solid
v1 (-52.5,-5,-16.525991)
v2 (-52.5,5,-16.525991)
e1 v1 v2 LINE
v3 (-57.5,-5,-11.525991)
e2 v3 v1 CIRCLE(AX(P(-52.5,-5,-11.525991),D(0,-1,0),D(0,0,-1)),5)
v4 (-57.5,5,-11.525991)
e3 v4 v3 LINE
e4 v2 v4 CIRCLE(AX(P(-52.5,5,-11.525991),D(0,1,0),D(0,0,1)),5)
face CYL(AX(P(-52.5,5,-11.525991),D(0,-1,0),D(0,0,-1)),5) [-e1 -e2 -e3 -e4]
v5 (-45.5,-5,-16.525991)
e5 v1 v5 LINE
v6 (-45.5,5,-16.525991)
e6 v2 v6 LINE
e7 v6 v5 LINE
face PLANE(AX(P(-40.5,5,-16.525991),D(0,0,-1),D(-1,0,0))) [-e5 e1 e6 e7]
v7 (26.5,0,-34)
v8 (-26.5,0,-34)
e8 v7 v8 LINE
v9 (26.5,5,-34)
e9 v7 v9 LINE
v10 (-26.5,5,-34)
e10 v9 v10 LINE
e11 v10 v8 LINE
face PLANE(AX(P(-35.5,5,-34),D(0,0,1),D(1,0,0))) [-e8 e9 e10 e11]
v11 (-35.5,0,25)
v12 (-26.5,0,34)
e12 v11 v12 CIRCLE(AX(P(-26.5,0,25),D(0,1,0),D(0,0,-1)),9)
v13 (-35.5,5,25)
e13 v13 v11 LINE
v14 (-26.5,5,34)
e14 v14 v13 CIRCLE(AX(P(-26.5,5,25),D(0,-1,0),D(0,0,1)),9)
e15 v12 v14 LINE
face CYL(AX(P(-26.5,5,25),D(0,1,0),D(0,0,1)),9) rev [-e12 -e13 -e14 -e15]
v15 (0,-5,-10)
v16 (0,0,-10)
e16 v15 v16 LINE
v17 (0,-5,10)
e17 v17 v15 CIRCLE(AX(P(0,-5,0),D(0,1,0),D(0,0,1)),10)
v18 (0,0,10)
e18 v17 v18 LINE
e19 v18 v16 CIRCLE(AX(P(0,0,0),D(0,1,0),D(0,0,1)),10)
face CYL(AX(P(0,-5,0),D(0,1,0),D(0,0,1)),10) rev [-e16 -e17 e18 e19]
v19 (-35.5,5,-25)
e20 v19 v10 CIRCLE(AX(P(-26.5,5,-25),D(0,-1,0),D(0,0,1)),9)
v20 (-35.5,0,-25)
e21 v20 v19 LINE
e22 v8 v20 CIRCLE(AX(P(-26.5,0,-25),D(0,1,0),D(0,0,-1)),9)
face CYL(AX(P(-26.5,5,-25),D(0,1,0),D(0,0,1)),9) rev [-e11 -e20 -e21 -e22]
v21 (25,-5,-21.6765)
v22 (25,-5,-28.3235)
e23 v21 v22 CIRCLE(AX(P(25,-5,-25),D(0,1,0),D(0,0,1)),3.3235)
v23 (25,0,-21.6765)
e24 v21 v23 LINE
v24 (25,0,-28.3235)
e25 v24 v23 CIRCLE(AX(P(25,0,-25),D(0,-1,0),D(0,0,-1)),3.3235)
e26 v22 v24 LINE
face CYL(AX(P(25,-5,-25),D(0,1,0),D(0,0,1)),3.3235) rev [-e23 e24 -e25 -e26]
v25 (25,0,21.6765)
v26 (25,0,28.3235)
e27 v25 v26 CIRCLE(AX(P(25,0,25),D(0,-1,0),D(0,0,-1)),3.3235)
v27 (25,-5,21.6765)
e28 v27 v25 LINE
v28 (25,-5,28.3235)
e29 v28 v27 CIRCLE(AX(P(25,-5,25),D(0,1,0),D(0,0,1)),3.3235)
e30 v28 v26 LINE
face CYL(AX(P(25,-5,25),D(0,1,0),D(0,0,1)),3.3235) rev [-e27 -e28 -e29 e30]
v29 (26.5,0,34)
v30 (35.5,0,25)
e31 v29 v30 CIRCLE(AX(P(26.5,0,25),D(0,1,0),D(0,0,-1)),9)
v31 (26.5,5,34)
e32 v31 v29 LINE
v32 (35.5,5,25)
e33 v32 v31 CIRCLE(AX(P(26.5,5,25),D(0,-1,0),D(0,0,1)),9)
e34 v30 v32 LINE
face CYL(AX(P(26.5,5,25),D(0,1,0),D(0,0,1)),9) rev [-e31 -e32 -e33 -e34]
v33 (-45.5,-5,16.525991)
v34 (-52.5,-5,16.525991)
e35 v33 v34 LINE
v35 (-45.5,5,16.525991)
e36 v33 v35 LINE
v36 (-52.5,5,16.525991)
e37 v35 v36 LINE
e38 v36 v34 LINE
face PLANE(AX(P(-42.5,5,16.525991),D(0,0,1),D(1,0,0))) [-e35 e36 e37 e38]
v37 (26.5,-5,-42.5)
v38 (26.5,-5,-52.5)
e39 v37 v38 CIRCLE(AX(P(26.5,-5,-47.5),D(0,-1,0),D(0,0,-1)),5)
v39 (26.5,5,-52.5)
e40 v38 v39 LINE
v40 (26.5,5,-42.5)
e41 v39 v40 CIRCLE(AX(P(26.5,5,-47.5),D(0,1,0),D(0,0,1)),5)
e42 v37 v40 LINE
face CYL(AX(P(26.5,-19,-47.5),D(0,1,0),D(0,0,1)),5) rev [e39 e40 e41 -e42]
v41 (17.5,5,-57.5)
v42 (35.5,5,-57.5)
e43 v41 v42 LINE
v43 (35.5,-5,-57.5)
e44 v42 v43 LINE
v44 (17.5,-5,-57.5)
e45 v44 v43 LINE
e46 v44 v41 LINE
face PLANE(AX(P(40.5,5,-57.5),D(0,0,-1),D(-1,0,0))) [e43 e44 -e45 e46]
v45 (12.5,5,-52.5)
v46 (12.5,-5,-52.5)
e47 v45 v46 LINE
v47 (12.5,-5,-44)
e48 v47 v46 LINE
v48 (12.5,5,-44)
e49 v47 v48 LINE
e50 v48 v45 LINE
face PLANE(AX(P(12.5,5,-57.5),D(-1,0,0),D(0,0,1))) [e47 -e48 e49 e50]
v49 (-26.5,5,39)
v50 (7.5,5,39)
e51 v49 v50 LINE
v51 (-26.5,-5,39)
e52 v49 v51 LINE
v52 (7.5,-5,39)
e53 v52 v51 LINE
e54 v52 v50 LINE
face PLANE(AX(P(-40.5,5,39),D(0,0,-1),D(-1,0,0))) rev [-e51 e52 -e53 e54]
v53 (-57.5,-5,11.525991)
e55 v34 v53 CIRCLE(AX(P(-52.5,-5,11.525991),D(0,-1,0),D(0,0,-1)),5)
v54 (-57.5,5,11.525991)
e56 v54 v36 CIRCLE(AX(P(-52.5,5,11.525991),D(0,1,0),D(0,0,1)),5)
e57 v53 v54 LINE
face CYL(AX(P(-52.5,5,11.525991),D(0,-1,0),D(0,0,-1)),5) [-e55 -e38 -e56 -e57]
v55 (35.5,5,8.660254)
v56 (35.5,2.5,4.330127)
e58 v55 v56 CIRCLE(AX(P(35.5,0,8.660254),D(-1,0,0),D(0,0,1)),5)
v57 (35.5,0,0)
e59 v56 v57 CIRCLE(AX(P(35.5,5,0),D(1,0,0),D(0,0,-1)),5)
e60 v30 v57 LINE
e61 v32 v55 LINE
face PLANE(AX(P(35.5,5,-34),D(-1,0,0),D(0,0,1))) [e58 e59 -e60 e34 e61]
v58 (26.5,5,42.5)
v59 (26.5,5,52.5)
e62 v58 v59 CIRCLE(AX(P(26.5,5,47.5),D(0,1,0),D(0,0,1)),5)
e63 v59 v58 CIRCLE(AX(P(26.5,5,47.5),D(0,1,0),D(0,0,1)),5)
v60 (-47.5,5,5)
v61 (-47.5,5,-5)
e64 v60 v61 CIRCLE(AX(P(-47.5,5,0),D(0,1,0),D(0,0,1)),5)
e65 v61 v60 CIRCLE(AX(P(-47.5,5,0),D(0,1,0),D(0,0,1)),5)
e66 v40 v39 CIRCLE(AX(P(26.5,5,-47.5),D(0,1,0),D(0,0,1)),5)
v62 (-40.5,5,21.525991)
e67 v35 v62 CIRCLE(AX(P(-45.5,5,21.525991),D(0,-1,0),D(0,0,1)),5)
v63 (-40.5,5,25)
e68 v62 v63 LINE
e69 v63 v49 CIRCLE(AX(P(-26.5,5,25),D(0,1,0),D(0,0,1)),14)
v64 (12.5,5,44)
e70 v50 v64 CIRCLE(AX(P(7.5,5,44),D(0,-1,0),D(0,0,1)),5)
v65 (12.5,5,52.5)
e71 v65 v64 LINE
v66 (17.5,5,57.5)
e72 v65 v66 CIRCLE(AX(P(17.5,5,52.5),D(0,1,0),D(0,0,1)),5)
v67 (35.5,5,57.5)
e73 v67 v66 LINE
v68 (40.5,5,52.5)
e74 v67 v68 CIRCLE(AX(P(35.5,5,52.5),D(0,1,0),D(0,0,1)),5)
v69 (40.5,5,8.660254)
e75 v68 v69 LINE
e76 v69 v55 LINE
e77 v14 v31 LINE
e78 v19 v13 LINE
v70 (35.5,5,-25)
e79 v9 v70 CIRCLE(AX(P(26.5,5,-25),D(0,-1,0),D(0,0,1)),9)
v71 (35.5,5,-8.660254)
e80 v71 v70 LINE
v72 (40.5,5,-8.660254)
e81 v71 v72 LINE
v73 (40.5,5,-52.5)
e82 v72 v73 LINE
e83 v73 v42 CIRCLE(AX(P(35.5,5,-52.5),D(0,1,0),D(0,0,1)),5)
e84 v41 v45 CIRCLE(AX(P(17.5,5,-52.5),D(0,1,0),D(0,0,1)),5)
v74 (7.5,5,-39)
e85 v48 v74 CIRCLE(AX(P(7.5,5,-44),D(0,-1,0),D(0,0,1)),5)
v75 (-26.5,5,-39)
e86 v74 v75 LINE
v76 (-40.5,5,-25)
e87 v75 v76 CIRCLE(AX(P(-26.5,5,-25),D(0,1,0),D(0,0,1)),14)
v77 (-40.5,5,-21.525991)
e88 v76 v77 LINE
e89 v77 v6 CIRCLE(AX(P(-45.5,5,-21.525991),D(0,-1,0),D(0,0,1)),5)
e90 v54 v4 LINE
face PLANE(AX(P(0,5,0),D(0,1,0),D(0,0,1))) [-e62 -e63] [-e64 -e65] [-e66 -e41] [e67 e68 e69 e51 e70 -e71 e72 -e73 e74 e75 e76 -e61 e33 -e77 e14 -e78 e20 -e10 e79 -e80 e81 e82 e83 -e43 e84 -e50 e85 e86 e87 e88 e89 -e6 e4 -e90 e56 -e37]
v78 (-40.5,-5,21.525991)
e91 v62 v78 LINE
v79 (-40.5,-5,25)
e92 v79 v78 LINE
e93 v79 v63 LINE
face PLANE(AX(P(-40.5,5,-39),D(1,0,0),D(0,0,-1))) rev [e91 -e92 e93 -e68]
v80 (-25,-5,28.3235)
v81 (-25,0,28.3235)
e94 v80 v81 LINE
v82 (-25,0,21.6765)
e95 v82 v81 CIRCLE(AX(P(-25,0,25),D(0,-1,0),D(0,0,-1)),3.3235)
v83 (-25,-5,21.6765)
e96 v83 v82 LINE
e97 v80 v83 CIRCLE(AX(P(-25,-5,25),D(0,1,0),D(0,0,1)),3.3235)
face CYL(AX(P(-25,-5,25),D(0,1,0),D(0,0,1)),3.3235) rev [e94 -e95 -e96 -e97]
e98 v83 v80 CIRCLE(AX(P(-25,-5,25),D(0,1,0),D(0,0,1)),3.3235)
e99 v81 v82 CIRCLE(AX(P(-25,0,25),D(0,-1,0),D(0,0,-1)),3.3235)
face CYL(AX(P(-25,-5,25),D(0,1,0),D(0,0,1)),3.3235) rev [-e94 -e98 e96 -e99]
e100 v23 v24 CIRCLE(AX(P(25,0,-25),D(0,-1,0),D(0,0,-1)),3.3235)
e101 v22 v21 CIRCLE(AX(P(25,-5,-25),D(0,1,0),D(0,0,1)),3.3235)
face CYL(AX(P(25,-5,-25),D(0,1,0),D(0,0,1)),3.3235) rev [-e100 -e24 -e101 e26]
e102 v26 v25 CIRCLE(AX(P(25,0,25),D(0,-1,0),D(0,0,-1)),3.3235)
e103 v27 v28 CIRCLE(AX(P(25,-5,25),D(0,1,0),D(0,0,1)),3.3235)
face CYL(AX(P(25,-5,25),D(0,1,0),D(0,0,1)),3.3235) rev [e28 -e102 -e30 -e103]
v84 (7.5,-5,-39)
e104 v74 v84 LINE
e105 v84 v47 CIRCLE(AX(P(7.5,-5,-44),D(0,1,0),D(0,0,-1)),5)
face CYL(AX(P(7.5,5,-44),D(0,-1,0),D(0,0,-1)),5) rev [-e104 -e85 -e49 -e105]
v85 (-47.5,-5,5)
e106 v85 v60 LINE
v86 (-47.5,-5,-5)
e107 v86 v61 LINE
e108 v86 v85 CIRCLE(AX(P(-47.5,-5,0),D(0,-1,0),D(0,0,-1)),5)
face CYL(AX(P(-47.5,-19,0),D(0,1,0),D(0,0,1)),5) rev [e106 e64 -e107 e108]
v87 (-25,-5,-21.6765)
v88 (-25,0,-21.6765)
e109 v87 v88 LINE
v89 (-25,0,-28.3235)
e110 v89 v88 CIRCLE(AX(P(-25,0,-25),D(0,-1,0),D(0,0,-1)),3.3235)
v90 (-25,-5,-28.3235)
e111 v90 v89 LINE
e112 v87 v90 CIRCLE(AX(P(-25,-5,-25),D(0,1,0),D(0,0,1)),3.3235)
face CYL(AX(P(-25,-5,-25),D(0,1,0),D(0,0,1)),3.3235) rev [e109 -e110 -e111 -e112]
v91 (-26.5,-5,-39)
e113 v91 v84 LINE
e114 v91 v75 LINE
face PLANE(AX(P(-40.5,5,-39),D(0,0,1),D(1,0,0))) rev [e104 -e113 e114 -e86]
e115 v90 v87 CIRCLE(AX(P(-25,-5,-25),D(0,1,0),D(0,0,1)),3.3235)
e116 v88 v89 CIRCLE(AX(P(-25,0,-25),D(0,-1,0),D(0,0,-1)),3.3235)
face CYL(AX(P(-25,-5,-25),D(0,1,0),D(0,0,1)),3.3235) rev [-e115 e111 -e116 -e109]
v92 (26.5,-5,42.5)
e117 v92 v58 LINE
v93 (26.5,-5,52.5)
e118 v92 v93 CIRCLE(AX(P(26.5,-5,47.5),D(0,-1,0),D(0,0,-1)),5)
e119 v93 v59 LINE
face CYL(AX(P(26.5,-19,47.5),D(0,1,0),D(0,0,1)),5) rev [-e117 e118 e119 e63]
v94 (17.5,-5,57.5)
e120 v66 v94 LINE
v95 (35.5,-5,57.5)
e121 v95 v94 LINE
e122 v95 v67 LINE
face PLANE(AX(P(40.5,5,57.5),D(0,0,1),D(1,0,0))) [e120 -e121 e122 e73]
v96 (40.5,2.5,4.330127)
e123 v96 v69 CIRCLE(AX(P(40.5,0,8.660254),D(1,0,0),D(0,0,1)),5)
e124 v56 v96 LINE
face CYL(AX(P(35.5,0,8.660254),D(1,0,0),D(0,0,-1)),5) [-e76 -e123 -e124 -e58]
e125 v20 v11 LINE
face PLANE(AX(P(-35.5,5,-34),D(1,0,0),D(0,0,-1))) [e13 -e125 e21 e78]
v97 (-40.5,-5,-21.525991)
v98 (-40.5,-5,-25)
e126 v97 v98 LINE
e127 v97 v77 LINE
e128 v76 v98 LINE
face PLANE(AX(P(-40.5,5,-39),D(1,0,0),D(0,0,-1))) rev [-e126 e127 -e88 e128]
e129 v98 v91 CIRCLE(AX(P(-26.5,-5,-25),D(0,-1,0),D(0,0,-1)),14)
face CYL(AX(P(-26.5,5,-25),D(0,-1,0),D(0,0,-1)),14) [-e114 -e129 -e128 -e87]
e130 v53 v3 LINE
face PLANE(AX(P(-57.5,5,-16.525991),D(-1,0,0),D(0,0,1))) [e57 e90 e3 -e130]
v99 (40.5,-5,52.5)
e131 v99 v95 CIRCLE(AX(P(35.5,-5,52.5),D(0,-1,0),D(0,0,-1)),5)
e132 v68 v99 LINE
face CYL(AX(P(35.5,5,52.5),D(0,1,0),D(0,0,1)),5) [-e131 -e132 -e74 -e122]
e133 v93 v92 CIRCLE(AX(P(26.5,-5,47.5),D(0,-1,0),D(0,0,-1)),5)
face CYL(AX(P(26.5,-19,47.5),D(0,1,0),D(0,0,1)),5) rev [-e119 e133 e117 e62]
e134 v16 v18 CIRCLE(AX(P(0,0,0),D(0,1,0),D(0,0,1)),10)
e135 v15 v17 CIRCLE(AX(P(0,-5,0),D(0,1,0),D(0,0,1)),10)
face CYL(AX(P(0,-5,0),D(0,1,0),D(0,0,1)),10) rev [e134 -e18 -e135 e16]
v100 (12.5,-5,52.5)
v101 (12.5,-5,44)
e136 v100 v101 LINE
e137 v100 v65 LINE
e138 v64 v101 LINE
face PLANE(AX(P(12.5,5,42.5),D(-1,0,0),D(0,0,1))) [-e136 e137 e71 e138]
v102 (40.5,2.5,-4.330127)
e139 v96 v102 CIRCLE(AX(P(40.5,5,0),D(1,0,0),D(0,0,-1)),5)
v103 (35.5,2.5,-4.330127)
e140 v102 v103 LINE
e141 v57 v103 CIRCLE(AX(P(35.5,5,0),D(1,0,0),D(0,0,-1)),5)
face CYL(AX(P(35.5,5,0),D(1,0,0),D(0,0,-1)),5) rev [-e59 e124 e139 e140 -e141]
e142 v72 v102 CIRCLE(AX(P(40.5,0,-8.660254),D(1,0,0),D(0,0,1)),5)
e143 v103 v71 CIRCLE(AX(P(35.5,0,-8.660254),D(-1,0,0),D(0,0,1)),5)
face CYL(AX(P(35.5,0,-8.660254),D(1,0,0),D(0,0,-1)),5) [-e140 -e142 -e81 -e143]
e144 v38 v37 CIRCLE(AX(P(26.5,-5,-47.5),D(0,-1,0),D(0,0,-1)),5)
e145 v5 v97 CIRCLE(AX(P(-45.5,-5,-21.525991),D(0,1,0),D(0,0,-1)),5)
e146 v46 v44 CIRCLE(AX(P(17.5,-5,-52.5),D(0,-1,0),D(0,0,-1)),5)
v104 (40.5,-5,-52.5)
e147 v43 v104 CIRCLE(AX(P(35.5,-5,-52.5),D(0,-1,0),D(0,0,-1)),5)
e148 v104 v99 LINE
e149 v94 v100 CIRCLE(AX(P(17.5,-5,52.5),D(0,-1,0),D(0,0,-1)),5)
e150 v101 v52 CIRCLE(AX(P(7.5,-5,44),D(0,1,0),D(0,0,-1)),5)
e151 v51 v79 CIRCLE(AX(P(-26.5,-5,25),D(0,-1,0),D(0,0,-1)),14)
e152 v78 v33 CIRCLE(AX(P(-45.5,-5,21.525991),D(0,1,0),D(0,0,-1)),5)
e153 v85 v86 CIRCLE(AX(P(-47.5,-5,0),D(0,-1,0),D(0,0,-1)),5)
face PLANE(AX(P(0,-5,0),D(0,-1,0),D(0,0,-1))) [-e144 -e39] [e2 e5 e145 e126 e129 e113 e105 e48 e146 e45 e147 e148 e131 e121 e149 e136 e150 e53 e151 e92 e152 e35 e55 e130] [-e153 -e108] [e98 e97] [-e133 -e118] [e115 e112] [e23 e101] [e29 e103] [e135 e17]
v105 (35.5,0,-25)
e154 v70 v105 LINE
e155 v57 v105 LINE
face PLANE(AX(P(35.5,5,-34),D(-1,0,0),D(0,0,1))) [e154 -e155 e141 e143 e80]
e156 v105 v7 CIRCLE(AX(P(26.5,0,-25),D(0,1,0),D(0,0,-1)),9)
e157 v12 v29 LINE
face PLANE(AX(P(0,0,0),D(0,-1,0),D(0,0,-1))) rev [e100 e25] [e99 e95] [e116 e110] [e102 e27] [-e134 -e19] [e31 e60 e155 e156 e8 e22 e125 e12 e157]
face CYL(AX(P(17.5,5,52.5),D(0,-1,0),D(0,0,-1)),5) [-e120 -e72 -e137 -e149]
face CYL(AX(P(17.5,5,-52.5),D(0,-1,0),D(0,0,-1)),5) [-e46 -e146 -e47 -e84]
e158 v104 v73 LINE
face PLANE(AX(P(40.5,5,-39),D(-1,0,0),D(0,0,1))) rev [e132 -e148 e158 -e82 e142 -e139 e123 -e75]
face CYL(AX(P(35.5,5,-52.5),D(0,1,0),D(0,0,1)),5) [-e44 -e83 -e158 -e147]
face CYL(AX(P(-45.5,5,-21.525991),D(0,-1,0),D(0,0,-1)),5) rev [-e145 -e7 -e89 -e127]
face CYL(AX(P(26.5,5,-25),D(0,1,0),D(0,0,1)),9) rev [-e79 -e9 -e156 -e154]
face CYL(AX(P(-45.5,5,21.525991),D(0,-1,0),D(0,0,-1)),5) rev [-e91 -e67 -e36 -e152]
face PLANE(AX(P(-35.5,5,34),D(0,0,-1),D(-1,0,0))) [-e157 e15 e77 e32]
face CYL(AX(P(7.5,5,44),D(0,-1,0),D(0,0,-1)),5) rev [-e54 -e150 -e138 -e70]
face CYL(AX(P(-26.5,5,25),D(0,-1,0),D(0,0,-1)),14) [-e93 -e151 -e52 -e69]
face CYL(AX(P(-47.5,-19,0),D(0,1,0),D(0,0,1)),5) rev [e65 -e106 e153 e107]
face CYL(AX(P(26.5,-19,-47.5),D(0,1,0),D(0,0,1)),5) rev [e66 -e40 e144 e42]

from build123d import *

# Parameters (mm, degrees)
SKETCH1_W           = 81
SKETCH1_H           = 78
SKETCH1_W_2         = 71
SKETCH1_H_2         = 68
BOSS_EXTRUDE1_DEPTH = 5
SKETCH2_W           = 81
SKETCH2_H           = 78
BOSS_EXTRUDE2_DEPTH = 5
BOSS_EXTRUDE3_DEPTH = 10
FILLET1_R           = 9
FILLET2_R           = 14
FILLET4_R           = 5
SKETCH4_R           = 10
CUT_EXTRUDE1_DEPTH  = 5
SKETCH5_R           = 5
CUT_EXTRUDE2_DEPTH  = 24
SKETCH6_R           = 5
CUT_EXTRUDE3_DEPTH  = 5
FILLET5_R           = 5
SKETCH7_R           = 3.3235
CUT_EXTRUDE4_DEPTH  = 10


with BuildPart() as part:
    # Sketch1 → Boss-Extrude1 (new body)
    with BuildSketch(Plane(origin=(0, 0, 0), x_dir=(1, 0, 0), z_dir=(0, 1, 0))):
        Rectangle(SKETCH1_W, SKETCH1_H)
        Rectangle(SKETCH1_W_2, SKETCH1_H_2, mode=Mode.SUBTRACT)
    extrude(amount=BOSS_EXTRUDE1_DEPTH)

    # Sketch2 → Boss-Extrude2 (add)
    with BuildSketch(Plane.XZ):
        Rectangle(SKETCH2_W, SKETCH2_H)
    extrude(amount=BOSS_EXTRUDE2_DEPTH)

    # Sketch3 → Boss-Extrude3 (add)
    with BuildSketch(Plane.XZ.offset(5)):
        Polygon((-42.5, 16.525991305), (-57.5, 16.525991305), (-57.5, 1.525991305), (-57.5, -1.525991305), (-57.5, -16.525991305), (-43.129437713, -16.525991305), (-40.5, -16.525991305), (-40.5, 16.525991305), align=None)
        Polygon((40.5, 57.5), (12.5, 57.5), (12.5, 42.5), (12.5, 39), (40.5, 39), align=None)
        Polygon((12.5, -39), (40.5, -39), (40.5, -57.5), (12.5, -57.5), (12.5, -42.5), align=None)
    extrude(amount=-BOSS_EXTRUDE3_DEPTH)

    # Fillet1
    fillet1_edges = [part.edges().sort_by_distance(p)[0] for p in [
        (35.5, 2.5, 34),
        (35.5, 2.5, -34),
        (-35.5, 2.5, -34),
        (-35.5, 2.5, 34),
    ]]
    fillet(fillet1_edges, radius=FILLET1_R)

    # Fillet2
    fillet2_edges = [part.edges().sort_by_distance(p)[0] for p in [
        (-40.5, 0, -39),
        (-40.5, 0, 39),
    ]]
    fillet(fillet2_edges, radius=FILLET2_R)

    # Fillet4
    fillet4_edges = [part.edges().sort_by_distance(p)[0] for p in [
        (-40.5, 0, 16.525991305),
        (-40.5, 0, -16.525991305),
        (-57.5, 0, -16.525991305),
        (-57.5, 0, 16.525991305),
        (12.5, 0, -39),
        (40.5, 0, -57.5),
        (12.5, 0, -57.5),
        (12.5, 0, 57.5),
        (40.5, 0, 57.5),
        (12.5, 0, 39),
    ]]
    fillet(fillet4_edges, radius=FILLET4_R)

    # Sketch4 → Cut-Extrude1 (cut)
    with BuildSketch(Plane(origin=(0, 0, 0), x_dir=(1, 0, 0), z_dir=(0, 1, 0))):
        with Locations(Location((0, 0, 0), (0, 0, 270))):
            Circle(SKETCH4_R)
    extrude(amount=-CUT_EXTRUDE1_DEPTH, mode=Mode.SUBTRACT)

    # Sketch5 → Cut-Extrude2 (cut)
    with BuildSketch(Plane(origin=(0, 5, 0), x_dir=(1, 0, 0), z_dir=(0, 1, 0))):
        with Locations(Location((26.5, 47.5, 0), (0, 0, 270))):
            Circle(SKETCH5_R)
        with Locations(Location((26.5, -47.5, 0), (0, 0, 270))):
            Circle(SKETCH5_R)
        with Locations(Location((-47.5, 0, 0), (0, 0, 270))):
            Circle(SKETCH5_R)
    extrude(amount=-CUT_EXTRUDE2_DEPTH, mode=Mode.SUBTRACT)

    # Sketch6 → Cut-Extrude3 (cut)
    with BuildSketch(Plane(origin=(40.5, 0, 0), x_dir=(0, 0, -1), z_dir=(1, 0, 0))):
        with Locations((0, 5)):
            Circle(SKETCH6_R)
    extrude(amount=-CUT_EXTRUDE3_DEPTH, mode=Mode.SUBTRACT)

    # Fillet5
    fillet5_edges = [part.edges().sort_by_distance(p)[0] for p in [
        (38, 5, 5),
        (38, 5, -5),
    ]]
    fillet(fillet5_edges, radius=FILLET5_R)

    # Sketch7 → Cut-Extrude4 (cut)
    with BuildSketch(Plane(origin=(0, 5, 0), x_dir=(1, 0, 0), z_dir=(0, 1, 0))):
        with Locations(Location((25, 25, 0), (0, 0, 270))):
            Circle(SKETCH7_R)
        with Locations(Location((-25, 25, 0), (0, 0, 270))):
            Circle(SKETCH7_R)
        with Locations(Location((-25, -25, 0), (0, 0, 270))):
            Circle(SKETCH7_R)
        with Locations(Location((25, -25, 0), (0, 0, 270))):
            Circle(SKETCH7_R)
    extrude(amount=-CUT_EXTRUDE4_DEPTH, mode=Mode.SUBTRACT)


solid = part.part
